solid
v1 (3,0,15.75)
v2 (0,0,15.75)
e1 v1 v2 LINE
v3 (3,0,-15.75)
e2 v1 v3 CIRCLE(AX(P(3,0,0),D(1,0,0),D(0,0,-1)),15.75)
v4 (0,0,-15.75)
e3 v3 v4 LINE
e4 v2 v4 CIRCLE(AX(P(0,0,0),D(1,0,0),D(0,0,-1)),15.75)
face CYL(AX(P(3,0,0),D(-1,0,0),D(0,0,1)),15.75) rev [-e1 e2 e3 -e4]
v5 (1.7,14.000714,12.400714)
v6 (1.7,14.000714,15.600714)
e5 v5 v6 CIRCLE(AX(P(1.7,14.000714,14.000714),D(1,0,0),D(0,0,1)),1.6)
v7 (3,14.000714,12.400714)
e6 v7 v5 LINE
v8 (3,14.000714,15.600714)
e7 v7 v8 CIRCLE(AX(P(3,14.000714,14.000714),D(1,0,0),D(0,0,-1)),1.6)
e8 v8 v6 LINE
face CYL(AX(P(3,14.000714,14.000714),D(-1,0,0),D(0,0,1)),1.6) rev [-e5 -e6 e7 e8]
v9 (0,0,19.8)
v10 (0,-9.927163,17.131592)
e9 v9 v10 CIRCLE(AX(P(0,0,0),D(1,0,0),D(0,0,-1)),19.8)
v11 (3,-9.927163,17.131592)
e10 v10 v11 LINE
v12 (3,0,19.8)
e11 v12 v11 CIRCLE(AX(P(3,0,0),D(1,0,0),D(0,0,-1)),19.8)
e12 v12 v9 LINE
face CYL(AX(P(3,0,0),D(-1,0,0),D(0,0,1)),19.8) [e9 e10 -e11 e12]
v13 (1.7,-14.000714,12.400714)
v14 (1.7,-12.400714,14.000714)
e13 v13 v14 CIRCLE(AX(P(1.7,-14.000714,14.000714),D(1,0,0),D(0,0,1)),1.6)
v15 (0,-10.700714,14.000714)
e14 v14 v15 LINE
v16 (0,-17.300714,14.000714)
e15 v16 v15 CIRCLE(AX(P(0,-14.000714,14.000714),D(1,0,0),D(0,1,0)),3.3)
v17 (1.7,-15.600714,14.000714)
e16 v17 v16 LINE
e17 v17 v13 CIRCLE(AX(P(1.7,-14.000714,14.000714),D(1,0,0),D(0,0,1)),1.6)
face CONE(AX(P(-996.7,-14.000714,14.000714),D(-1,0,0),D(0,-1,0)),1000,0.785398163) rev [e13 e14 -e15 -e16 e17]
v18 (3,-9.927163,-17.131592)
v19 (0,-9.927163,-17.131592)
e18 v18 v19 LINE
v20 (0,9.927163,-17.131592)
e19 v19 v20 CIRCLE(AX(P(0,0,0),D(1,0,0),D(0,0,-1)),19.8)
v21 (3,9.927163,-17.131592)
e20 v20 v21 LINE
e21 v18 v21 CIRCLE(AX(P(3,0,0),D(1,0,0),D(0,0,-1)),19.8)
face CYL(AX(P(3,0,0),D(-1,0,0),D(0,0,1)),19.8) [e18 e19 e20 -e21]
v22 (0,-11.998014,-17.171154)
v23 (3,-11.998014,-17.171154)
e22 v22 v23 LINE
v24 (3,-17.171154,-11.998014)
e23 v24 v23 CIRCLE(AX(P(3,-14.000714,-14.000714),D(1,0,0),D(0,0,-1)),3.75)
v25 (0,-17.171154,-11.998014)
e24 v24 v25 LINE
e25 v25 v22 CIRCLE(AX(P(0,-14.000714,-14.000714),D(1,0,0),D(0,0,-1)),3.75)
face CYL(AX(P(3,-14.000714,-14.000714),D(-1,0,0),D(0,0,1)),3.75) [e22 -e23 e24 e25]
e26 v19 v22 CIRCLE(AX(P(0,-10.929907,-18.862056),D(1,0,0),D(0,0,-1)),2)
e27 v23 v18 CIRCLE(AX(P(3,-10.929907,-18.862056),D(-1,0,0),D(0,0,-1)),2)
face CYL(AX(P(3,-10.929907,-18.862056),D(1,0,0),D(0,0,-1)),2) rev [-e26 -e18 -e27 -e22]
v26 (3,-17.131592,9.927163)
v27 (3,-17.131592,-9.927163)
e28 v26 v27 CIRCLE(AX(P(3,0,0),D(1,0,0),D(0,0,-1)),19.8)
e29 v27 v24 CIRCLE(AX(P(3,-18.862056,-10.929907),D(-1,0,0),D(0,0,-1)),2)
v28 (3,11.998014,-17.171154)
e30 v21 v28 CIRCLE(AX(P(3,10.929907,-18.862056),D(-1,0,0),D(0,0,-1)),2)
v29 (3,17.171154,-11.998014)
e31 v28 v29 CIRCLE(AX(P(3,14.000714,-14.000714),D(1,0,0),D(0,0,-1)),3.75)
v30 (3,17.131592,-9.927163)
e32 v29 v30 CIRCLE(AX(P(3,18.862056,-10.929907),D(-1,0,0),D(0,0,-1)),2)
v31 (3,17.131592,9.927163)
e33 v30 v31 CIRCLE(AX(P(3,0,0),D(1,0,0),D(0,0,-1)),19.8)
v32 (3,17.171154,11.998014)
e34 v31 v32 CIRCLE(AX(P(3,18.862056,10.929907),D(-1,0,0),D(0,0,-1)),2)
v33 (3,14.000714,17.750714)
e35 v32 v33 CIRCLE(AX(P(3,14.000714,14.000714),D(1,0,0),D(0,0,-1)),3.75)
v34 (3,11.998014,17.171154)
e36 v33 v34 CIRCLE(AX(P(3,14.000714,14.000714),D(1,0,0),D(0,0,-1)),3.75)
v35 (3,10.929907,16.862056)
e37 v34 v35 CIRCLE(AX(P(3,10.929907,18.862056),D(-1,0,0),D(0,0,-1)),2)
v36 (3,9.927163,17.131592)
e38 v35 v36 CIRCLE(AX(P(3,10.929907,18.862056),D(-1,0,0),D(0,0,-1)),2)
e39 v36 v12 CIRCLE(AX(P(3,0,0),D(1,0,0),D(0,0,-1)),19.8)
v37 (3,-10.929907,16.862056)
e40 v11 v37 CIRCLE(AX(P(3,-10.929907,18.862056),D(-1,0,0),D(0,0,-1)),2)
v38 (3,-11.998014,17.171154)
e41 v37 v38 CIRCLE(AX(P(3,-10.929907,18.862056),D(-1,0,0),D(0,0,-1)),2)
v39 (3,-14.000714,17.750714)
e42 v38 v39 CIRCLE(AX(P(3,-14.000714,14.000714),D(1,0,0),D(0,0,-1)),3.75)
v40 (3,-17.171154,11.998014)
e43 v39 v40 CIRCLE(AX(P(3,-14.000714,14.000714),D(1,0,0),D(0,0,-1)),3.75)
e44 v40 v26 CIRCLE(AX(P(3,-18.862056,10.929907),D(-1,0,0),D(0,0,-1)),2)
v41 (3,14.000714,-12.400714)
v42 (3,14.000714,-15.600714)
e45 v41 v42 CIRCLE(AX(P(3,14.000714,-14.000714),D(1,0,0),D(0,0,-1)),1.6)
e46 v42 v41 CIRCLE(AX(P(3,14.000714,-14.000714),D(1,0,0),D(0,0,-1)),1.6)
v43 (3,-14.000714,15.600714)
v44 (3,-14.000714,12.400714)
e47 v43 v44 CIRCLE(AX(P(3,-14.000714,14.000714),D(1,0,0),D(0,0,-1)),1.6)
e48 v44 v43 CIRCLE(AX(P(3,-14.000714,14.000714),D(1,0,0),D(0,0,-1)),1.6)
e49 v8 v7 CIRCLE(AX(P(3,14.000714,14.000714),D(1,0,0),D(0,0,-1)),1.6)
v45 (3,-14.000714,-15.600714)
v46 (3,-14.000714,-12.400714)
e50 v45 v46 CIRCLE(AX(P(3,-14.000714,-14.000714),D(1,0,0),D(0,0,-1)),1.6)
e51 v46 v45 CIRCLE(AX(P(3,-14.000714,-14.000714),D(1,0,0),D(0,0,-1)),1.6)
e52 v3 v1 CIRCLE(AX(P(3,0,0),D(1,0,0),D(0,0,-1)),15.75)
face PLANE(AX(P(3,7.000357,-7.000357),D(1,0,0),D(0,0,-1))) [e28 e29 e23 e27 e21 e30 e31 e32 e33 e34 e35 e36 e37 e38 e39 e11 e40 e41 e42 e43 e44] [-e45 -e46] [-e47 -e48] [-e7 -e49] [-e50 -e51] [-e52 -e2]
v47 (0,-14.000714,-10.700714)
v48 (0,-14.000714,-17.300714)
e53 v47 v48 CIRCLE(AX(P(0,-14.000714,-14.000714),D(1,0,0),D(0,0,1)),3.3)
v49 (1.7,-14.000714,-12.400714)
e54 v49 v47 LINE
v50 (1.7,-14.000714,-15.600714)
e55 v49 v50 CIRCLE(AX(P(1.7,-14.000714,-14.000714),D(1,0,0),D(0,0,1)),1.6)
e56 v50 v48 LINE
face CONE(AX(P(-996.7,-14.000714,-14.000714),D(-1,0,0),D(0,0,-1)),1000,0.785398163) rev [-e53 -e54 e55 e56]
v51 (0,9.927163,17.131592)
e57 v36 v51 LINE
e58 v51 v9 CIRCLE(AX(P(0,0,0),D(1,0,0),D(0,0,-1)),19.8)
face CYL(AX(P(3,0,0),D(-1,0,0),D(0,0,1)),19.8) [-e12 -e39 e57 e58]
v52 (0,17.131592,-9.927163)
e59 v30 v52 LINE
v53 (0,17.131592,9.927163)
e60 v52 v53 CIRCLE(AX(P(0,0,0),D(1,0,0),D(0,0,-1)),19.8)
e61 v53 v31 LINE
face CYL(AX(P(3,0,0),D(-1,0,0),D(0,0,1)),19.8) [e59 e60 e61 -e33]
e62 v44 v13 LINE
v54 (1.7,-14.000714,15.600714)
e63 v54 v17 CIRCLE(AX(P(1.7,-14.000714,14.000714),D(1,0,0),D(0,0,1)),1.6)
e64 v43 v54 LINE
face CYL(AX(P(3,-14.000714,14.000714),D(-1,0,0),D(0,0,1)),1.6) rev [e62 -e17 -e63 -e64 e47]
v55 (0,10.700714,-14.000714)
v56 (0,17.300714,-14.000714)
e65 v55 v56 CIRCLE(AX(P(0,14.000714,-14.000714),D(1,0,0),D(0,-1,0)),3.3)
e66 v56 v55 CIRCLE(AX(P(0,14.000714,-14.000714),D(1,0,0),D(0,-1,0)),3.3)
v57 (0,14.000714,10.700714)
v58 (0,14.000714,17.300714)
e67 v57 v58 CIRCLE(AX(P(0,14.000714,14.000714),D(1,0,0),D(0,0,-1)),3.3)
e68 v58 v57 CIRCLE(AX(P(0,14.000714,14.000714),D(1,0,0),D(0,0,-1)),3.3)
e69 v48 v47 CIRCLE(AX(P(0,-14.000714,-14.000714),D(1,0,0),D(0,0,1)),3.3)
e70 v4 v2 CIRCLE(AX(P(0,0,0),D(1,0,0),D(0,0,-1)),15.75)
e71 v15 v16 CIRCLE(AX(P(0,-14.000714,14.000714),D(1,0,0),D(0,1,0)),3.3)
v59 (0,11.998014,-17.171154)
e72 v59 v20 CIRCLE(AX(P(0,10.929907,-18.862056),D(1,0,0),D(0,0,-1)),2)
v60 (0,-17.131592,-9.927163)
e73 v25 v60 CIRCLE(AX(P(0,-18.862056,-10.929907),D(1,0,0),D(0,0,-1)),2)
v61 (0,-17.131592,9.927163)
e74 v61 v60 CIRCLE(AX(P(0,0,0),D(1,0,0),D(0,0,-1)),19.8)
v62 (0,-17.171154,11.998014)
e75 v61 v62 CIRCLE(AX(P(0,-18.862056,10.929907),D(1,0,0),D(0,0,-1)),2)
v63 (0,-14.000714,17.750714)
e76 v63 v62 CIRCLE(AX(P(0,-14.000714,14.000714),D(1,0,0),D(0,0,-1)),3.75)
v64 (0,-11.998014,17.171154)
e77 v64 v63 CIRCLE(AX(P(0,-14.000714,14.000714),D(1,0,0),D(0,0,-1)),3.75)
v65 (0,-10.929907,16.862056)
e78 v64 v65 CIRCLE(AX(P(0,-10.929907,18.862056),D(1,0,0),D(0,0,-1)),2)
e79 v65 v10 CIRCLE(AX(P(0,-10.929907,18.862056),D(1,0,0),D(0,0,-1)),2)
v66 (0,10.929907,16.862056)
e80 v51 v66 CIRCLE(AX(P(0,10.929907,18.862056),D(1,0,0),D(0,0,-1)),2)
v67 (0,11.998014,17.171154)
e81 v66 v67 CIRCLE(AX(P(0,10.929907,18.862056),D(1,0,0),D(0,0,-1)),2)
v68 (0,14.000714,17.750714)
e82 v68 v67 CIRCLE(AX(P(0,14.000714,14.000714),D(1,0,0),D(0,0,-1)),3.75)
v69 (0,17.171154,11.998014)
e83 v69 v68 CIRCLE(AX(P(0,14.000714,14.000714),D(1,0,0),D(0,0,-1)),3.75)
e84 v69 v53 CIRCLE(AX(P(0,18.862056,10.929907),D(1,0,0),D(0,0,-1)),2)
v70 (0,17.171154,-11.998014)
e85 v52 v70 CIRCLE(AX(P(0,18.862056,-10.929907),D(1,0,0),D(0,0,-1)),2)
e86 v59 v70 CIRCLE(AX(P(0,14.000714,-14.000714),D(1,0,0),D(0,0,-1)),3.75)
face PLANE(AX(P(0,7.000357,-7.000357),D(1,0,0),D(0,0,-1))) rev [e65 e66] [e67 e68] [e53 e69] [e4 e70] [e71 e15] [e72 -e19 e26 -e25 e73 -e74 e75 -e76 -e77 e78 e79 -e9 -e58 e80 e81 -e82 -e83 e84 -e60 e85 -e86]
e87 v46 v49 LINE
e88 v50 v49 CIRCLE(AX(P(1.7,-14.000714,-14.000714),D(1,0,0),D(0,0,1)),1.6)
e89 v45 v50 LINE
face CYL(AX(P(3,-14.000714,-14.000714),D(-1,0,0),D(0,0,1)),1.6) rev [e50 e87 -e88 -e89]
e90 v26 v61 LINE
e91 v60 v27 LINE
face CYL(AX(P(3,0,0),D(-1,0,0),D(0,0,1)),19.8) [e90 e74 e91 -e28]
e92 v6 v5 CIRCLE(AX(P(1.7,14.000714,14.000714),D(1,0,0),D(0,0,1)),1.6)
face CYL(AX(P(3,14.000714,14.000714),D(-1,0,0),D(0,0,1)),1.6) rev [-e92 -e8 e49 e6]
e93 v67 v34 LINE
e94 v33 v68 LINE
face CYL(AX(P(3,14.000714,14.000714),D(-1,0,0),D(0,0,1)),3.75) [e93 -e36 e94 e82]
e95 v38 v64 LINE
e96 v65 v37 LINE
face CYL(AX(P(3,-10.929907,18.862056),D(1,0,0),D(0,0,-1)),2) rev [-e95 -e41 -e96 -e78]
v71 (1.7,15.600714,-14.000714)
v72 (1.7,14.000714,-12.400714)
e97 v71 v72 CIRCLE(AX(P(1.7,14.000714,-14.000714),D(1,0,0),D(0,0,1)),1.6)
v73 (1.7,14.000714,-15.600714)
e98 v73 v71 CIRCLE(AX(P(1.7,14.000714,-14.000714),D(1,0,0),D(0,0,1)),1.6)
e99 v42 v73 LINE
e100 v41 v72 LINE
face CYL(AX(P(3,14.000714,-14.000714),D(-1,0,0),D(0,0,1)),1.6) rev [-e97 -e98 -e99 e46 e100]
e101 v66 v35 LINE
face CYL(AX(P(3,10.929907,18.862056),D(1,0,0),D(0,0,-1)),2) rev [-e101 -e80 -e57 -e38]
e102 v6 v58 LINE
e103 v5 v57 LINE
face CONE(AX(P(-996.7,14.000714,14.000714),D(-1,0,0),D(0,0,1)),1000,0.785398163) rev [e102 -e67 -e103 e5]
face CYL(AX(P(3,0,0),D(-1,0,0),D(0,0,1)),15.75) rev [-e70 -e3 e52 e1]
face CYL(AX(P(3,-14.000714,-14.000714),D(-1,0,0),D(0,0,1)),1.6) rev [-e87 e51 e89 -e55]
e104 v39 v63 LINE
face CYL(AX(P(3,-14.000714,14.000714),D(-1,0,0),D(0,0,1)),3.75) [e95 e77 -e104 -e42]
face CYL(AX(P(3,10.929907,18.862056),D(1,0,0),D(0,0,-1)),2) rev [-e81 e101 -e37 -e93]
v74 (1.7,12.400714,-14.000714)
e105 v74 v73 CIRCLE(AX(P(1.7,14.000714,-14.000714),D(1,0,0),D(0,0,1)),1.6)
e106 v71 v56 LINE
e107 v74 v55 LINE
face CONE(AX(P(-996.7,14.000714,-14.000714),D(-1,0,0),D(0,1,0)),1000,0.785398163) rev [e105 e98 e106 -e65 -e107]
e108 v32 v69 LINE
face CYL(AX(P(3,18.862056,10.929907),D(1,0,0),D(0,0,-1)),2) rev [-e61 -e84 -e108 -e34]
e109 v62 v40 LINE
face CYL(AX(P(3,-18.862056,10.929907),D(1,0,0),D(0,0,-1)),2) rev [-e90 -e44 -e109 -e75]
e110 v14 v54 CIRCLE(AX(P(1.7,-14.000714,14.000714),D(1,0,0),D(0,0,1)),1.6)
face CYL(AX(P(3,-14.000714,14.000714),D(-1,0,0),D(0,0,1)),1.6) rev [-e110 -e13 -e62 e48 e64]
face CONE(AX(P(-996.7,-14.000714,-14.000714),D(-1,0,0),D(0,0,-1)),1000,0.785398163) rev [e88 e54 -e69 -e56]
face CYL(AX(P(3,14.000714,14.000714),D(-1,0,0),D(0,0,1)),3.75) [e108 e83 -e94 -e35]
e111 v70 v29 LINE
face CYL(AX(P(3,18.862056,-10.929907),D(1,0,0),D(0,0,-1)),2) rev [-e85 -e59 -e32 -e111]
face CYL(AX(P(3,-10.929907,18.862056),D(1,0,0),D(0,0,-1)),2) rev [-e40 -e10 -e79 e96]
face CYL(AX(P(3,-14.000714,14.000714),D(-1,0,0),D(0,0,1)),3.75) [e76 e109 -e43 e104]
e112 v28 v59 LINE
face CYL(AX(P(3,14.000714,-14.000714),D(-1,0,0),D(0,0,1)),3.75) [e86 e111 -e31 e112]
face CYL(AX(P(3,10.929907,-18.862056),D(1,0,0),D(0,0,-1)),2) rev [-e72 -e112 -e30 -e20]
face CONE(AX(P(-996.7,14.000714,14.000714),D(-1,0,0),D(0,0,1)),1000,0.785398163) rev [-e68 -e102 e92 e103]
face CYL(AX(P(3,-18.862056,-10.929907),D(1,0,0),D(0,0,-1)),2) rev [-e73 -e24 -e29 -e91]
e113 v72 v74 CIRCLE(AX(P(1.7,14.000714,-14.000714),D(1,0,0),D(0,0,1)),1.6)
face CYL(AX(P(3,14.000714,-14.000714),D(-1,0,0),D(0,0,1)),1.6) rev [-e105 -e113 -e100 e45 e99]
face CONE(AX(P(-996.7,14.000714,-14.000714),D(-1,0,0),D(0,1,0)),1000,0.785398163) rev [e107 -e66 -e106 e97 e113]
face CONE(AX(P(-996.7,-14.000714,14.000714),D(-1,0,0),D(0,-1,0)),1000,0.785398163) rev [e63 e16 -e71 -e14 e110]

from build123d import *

# Parameters (mm, degrees)
SKETCH_1_R               = 15.75
SKETCH_1_R_2             = 1.6
EXTRUDE_1_DEPTH          = 3
PATTERN_CIRCULAR_1_COUNT = 4
FILLET_1_R               = 2


with BuildPart() as part:
    # 草图1 → 凸台-拉伸1 (new body)
    with BuildSketch(Plane(origin=(0, 0, 0), x_dir=(0, 0, -1), z_dir=(1, 0, 0))):
        with BuildLine():
            ThreePointArc((-16.389345303, 11.109876711), (-19.8, 0), (-16.389345303, -11.109876711))
            ThreePointArc((-16.389345303, -11.109876711), (-16.652364697, -16.652364697), (-11.109876711, -16.389345303))
            ThreePointArc((-11.109876711, -16.389345303), (0, -19.8), (11.109876711, -16.389345303))
            ThreePointArc((11.109876711, -16.389345303), (16.652364697, -16.652364697), (16.389345303, -11.109876711))
            ThreePointArc((16.389345303, -11.109876711), (19.8, 0), (16.389345303, 11.109876711))
            ThreePointArc((16.389345303, 11.109876711), (16.652364697, 16.652364697), (11.109876711, 16.389345303))
            ThreePointArc((11.109876711, 16.389345303), (0, 19.8), (-11.109876711, 16.389345303))
            ThreePointArc((-11.109876711, 16.389345303), (-16.652364697, 16.652364697), (-16.389345303, 11.109876711))
        make_face()
        Circle(SKETCH_1_R, mode=Mode.SUBTRACT)
        with Locations((14.000714267, -14.000714267)):
            Circle(SKETCH_1_R_2, mode=Mode.SUBTRACT)
        with Locations((-14.000714267, -14.000714267)):
            Circle(SKETCH_1_R_2, mode=Mode.SUBTRACT)
        with Locations((-14.000714267, 14.000714267)):
            Circle(SKETCH_1_R_2, mode=Mode.SUBTRACT)
        with Locations((14.000714267, 14.000714267)):
            Circle(SKETCH_1_R_2, mode=Mode.SUBTRACT)
    extrude(amount=EXTRUDE_1_DEPTH)

    # 草图2 → 切除-旋转1 (revolve, cut)
    with BuildSketch(Plane(origin=(0, 0, 0), x_dir=(1, 0, 0), z_dir=(0, -0.7071067811865581, 0.707106781186537)), mode=Mode.PRIVATE) as cut_revolve_1_sk:
        Polygon((0, 19.8), (0, 23.1), (3.3, 19.8), align=None)
    cut_revolve_1 = revolve(cut_revolve_1_sk.sketch.rotate(Axis((3.3, 14.000714267, 14.000714267), (-1, 0, 0)), 315), axis=Axis((3.3, 14.000714267, 14.000714267), (-1, 0, 0)), mode=Mode.SUBTRACT)

    # 阵列(圆周)1: 切除-旋转1 ×4 about axis
    pattern_circular_1_axis = Axis((0, 0, 0), (1, 0, 0))
    for i in range(1, PATTERN_CIRCULAR_1_COUNT):
        add(cut_revolve_1.rotate(pattern_circular_1_axis, i * 360 / PATTERN_CIRCULAR_1_COUNT), mode=Mode.SUBTRACT)

    # 圆角1
    fillet_1_edges = [part.edges().sort_by_distance(p)[0] for p in [
        (1.5, -11.109876711, -16.389345303),
        (1.5, -16.389345303, -11.109876711),
        (1.5, -16.389345303, 11.109876711),
        (1.5, -11.109876711, 16.389345303),
        (1.5, 11.109876711, 16.389345303),
        (1.5, 16.389345303, 11.109876711),
        (1.5, 16.389345303, -11.109876711),
        (1.5, 11.109876711, -16.389345303),
    ]]
    fillet(fillet_1_edges, radius=FILLET_1_R)


solid = part.part
